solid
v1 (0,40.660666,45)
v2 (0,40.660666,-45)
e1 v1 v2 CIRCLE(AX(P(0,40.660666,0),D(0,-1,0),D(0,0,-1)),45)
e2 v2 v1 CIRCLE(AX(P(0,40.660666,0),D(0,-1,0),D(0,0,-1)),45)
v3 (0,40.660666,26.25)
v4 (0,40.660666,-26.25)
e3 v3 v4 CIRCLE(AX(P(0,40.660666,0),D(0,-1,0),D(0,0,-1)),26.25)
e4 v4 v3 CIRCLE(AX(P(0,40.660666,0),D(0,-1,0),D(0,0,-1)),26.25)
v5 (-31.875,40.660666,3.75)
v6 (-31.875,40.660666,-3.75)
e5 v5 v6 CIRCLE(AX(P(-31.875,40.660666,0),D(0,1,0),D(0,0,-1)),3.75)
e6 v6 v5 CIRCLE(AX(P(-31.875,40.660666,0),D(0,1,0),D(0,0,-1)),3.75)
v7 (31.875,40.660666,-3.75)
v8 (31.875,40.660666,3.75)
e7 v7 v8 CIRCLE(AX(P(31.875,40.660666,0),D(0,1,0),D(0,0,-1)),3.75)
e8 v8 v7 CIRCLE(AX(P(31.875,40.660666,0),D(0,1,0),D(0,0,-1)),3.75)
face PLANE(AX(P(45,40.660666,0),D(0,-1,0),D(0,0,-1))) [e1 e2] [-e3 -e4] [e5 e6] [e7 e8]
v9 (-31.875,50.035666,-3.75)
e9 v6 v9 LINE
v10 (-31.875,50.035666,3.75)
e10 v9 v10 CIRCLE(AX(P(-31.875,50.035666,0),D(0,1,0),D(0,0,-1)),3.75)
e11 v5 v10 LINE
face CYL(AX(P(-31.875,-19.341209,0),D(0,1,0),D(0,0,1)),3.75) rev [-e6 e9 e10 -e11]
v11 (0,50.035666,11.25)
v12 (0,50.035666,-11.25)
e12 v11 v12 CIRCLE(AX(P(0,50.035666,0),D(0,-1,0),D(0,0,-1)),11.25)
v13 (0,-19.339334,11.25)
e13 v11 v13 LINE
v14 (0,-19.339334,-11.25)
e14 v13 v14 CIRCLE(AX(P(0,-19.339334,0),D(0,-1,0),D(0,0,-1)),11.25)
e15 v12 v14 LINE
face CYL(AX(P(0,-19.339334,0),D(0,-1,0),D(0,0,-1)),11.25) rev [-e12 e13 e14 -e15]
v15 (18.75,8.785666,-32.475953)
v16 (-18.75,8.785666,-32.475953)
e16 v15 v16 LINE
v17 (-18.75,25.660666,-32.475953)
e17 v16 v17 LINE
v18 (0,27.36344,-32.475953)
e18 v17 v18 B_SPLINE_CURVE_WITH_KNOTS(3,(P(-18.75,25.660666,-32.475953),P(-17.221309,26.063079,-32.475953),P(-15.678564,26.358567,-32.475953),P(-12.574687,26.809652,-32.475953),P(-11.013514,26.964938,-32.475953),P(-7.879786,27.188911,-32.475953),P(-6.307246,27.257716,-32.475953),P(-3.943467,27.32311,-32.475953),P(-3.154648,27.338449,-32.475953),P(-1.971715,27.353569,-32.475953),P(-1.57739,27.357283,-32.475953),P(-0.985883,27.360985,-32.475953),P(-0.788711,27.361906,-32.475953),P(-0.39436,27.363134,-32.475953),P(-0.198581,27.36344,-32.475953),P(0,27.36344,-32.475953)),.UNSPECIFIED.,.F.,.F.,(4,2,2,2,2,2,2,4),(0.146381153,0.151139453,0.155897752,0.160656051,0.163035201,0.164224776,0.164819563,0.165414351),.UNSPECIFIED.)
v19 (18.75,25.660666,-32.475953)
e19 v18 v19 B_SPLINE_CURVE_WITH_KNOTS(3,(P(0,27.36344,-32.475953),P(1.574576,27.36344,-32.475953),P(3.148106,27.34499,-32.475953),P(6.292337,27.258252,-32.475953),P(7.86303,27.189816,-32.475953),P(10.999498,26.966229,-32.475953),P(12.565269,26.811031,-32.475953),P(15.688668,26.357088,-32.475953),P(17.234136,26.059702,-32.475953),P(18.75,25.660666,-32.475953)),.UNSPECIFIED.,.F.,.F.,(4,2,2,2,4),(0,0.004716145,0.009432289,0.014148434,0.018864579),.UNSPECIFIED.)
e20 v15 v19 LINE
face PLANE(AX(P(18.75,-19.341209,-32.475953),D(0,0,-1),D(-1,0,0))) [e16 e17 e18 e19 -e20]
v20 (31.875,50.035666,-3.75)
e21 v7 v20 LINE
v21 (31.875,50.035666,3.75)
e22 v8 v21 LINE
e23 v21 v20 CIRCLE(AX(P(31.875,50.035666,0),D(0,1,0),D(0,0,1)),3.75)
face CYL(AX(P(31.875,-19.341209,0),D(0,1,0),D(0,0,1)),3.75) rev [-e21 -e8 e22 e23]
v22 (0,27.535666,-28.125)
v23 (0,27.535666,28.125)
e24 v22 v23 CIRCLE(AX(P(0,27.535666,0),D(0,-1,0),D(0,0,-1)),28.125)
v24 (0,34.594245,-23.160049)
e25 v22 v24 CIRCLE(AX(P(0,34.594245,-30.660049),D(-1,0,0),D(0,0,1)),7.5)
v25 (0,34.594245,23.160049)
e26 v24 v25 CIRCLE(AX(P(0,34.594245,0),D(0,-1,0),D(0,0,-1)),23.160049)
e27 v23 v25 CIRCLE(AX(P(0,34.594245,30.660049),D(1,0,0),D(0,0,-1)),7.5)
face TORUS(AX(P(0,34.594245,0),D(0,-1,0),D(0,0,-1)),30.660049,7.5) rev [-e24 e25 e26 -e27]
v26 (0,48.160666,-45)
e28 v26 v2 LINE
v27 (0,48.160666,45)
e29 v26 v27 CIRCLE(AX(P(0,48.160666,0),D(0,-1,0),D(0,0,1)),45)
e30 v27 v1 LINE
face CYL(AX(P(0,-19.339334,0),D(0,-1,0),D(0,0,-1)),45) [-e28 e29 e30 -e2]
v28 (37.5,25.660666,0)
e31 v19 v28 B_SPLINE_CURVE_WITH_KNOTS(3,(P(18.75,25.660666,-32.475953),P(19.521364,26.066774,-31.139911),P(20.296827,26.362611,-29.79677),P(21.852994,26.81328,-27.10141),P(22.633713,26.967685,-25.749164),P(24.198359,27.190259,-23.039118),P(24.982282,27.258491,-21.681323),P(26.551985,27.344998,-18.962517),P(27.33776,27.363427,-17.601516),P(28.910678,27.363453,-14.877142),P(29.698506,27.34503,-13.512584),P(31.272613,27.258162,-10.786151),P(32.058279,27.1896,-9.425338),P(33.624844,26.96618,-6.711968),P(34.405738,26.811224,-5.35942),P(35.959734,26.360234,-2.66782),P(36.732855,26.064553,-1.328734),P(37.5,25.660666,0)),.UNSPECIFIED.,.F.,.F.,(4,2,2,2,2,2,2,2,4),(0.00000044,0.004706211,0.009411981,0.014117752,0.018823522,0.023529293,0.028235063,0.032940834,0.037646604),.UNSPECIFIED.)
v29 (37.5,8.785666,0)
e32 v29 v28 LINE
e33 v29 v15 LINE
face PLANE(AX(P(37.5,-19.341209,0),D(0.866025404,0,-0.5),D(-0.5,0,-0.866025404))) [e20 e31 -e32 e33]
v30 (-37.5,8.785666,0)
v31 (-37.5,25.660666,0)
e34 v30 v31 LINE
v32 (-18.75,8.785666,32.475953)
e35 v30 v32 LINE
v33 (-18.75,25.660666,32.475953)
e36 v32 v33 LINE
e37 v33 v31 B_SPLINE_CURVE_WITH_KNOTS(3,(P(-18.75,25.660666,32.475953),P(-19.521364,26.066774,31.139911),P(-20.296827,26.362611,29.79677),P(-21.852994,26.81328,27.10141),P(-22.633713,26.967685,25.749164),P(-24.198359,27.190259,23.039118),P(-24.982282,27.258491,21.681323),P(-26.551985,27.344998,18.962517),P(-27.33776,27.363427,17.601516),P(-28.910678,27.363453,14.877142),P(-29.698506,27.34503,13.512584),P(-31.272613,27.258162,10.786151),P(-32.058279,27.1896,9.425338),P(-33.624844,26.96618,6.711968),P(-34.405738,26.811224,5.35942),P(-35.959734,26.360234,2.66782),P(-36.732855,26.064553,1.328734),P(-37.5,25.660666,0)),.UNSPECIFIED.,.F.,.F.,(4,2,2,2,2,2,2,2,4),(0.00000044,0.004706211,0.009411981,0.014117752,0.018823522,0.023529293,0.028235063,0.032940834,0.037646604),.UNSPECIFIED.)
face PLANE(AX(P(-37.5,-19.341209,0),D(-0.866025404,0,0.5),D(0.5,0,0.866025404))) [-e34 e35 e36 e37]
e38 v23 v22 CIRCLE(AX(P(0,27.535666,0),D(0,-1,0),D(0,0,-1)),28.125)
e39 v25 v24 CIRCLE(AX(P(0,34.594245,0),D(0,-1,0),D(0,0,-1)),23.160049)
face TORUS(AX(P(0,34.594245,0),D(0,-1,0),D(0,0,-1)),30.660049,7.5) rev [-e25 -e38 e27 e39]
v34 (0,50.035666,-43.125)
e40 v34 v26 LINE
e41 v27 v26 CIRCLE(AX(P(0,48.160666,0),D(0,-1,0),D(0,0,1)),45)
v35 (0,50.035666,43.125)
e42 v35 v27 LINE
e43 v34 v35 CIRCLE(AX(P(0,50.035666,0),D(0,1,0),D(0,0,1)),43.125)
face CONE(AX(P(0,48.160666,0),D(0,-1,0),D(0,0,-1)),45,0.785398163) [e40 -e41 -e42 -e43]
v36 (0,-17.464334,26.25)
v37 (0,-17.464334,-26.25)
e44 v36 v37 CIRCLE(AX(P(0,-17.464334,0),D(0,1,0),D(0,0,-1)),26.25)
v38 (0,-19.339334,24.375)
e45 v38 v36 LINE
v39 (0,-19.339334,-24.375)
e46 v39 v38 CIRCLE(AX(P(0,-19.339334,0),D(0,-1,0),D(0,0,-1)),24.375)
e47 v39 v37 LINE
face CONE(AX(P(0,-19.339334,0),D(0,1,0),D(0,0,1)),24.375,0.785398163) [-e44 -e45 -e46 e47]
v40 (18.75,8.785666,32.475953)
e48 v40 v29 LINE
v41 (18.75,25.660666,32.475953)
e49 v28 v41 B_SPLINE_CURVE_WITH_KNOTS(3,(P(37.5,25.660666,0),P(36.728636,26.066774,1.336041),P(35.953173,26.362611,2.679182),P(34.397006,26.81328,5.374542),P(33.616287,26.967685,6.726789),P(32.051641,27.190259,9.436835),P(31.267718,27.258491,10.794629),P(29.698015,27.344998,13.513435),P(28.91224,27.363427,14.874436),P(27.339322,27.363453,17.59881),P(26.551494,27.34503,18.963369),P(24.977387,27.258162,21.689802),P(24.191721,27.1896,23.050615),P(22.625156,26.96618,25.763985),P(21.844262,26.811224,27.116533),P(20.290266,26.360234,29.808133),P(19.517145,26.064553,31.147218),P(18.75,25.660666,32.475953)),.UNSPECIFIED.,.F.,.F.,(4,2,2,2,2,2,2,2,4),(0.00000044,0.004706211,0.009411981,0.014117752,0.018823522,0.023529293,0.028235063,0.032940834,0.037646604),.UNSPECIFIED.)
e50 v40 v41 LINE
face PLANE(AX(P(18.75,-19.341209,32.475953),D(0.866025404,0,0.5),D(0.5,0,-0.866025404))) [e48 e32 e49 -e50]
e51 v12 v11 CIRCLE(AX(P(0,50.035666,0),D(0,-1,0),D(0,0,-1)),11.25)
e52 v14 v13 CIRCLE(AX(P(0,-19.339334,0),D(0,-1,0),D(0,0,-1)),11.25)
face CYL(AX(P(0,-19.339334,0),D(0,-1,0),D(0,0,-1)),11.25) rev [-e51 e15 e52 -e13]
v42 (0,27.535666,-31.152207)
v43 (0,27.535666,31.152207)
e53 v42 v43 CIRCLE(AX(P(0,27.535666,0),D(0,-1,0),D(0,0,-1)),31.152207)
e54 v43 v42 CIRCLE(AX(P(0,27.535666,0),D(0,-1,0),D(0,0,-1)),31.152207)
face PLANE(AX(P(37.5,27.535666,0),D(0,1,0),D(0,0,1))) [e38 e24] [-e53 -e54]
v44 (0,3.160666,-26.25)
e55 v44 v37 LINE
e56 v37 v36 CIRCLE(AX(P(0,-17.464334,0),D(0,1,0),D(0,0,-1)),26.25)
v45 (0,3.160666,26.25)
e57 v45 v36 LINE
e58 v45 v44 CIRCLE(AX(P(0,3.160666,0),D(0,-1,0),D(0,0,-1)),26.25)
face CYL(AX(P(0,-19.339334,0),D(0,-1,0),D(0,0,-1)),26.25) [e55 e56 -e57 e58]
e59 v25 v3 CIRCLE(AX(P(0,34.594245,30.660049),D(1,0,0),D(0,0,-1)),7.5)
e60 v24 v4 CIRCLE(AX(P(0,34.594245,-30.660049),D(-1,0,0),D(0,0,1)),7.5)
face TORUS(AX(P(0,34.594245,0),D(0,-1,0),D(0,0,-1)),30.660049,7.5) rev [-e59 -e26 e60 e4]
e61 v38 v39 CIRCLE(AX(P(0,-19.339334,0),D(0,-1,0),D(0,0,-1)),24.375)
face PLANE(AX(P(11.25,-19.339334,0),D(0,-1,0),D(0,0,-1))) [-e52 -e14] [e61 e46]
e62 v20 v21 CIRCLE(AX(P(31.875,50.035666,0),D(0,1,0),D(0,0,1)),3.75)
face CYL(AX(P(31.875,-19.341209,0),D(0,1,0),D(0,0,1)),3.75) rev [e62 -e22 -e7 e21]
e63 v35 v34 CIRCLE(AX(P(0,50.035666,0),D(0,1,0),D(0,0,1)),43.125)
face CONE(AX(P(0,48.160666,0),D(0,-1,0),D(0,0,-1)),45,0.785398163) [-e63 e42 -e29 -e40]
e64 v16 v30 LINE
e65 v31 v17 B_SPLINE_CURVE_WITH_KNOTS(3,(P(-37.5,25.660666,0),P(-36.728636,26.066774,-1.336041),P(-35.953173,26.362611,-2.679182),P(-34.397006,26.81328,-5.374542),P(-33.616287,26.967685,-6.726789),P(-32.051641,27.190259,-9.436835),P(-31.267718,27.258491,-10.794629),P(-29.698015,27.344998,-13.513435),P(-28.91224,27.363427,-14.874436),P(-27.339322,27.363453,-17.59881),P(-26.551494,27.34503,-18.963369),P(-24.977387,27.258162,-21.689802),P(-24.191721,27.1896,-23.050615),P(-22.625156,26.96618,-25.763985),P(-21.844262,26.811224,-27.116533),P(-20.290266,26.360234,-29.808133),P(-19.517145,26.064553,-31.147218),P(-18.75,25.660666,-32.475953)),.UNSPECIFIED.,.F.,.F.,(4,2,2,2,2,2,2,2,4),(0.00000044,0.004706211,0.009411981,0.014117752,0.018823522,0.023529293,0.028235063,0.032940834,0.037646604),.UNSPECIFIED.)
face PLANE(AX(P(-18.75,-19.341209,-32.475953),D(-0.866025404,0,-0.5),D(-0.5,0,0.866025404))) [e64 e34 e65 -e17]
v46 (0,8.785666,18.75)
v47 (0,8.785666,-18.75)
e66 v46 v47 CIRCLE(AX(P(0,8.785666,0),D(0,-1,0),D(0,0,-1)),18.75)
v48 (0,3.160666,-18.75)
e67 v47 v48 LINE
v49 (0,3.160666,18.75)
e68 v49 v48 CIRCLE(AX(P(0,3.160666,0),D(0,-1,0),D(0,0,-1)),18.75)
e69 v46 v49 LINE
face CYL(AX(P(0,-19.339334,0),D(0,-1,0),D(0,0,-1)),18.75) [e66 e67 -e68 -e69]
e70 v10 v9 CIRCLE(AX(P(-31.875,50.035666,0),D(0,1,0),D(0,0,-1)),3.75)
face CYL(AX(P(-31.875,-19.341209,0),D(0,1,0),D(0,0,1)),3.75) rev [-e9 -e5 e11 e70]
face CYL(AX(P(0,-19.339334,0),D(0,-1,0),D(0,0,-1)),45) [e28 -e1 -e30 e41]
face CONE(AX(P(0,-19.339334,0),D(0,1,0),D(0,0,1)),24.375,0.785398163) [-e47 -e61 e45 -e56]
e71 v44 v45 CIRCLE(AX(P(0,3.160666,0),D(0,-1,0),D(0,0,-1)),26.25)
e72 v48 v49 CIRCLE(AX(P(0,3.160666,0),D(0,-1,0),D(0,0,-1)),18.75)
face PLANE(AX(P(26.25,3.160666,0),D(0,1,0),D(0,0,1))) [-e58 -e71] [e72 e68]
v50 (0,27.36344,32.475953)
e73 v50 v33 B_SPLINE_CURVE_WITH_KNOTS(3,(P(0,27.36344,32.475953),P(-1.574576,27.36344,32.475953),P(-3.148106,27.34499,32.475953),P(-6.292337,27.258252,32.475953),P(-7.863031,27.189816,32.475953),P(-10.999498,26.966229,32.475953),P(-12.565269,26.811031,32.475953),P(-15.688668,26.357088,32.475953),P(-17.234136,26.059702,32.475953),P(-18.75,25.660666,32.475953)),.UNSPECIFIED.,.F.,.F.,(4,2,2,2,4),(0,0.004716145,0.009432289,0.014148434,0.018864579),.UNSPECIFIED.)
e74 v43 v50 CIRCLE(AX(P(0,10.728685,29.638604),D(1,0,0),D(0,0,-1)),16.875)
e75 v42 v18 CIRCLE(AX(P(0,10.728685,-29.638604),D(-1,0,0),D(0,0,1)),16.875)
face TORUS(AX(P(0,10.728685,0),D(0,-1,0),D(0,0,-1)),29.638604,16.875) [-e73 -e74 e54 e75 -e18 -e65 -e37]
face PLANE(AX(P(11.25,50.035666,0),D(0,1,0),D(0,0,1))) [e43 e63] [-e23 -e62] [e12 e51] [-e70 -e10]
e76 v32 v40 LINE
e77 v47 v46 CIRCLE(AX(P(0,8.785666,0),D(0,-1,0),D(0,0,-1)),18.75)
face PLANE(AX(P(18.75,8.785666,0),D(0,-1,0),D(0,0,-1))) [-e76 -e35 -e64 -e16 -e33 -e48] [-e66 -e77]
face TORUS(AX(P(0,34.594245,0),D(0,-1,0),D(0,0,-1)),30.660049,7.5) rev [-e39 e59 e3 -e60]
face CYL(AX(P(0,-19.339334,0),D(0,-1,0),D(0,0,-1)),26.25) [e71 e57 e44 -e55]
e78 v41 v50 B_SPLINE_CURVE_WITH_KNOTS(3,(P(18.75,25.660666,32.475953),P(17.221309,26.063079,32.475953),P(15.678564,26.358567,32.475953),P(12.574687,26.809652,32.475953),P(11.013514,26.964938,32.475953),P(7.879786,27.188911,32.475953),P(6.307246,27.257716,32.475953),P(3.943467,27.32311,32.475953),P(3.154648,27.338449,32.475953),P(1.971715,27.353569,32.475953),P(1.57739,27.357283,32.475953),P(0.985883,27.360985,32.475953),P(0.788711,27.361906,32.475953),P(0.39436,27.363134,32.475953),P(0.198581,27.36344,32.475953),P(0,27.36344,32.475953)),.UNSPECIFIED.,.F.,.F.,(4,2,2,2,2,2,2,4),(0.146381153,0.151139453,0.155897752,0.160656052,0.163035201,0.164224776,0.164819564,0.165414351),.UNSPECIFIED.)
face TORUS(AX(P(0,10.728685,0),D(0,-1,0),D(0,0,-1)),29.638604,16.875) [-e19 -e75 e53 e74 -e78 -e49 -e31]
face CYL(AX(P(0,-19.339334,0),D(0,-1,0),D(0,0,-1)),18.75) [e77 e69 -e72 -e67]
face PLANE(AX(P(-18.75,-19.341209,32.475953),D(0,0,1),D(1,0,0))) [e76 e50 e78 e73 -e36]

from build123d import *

# Parameters (mm, degrees)
CHAMFER2_SIZE      = 1
CUT_EXTRUDE1_START = -10
SKETCH2_R          = 31.378818645
CUT_EXTRUDE1_DEPTH = 10
CHAMFER3_SIZE      = 1
CUT_EXTRUDE2_REACH = 52.21
SKETCH4_R          = 2
SCALE_1_SCALE      = 1.875


with BuildPart() as part:
    # Sketch1 → Revolve2 (revolve)
    with BuildSketch(Plane.XY, mode=Mode.PRIVATE) as revolve2_sk:
        with BuildLine():
            Line((6, 0), (6, 37))
            Line((6, 37), (24, 37))
            Line((24, 37), (24, 32))
            Line((24, 32), (14, 32))
            ThreePointArc((14, 32), (12.392227943, 28.198889706), (15, 25))
            Line((15, 25), (20, 25))
            Line((20, 25), (20, 15))
            Line((20, 15), (10, 15))
            Line((10, 15), (10, 12))
            Line((10, 12), (14, 12))
            Line((14, 12), (14, 0))
            Line((14, 0), (6, 0))
        make_face()
    revolve(revolve2_sk.sketch.rotate(Axis((0, 0, 0), (0, 1, 0)), 90), axis=Axis((0, 0, 0), (0, 1, 0)))

    # Chamfer2
    chamfer2_edges = [part.edges().sort_by_distance(p)[0] for p in [
        (0, 0, 14),
    ]]
    chamfer(chamfer2_edges, length=CHAMFER2_SIZE)

    # Sketch2 → Cut-Extrude1 (cut)
    with BuildSketch(Plane(origin=(0, 25, 0), x_dir=(1, 0, 0), z_dir=(0, 1, 0)).offset(CUT_EXTRUDE1_START)):
        Circle(SKETCH2_R)
        Polygon((20, 0), (10, 17.320508076), (-10, 17.320508076), (-20, 0), (-10, -17.320508076), (10, -17.320508076), align=None, mode=Mode.SUBTRACT)
    extrude(amount=CUT_EXTRUDE1_DEPTH, mode=Mode.SUBTRACT)

    # Sketch3 → Cut-Revolve1 (revolve, cut)
    with BuildSketch(Plane.XY, mode=Mode.PRIVATE) as cut_revolve1_sk:
        with BuildLine():
            Line((-20, 24), (-20, 25))
            Line((-20, 25), (-16.614510602, 25))
            ThreePointArc((-16.614510602, 25), (-18.356765058, 24.667614757), (-20, 24))
        make_face()
    revolve(cut_revolve1_sk.sketch.rotate(Axis((0, 0, 0), (0, 1, 0)), 270), axis=Axis((0, 0, 0), (0, 1, 0)), mode=Mode.SUBTRACT)

    # Chamfer3
    chamfer3_edges = [part.edges().sort_by_distance(p)[0] for p in [
        (0, 37, 24),
    ]]
    chamfer(chamfer3_edges, length=CHAMFER3_SIZE)

    # Sketch4 → Cut-Extrude2 (cut, up to next)
    with BuildSketch(Plane(origin=(0, 37, 0), x_dir=(1, 0, 0), z_dir=(0, 1, 0)), mode=Mode.PRIVATE) as cut_extrude2_sk1:
        with Locations(Location((17, 0, 0), (0, 0, 270))):
            Circle(SKETCH4_R)
    cut_extrude2_tool1 = extrude(cut_extrude2_sk1.sketch, amount=-CUT_EXTRUDE2_REACH, mode=Mode.PRIVATE) & part.part
    # Sketch4 → Cut-Extrude2 (cut, up to next)
    with BuildSketch(Plane(origin=(0, 37, 0), x_dir=(1, 0, 0), z_dir=(0, 1, 0)), mode=Mode.PRIVATE) as cut_extrude2_sk2:
        with Locations(Location((-17, 0, 0), (0, 0, 90))):
            Circle(SKETCH4_R)
    cut_extrude2_tool2 = extrude(cut_extrude2_sk2.sketch, amount=-CUT_EXTRUDE2_REACH, mode=Mode.PRIVATE) & part.part
    add(cut_extrude2_tool1.solids().sort_by_distance((17, 37, 0))[0], mode=Mode.SUBTRACT)
    add(cut_extrude2_tool2.solids().sort_by_distance((-17, 37, 0))[0], mode=Mode.SUBTRACT)


with BuildPart() as part_1:
    # Scale 1: scaled about (-3.12e-07, 22.102096906, 1.9e-08)
    add(part.part.scale(SCALE_1_SCALE).moved(Location((2.73e-07, -19.339334793, -1.7e-08))))


solid = part_1.part
